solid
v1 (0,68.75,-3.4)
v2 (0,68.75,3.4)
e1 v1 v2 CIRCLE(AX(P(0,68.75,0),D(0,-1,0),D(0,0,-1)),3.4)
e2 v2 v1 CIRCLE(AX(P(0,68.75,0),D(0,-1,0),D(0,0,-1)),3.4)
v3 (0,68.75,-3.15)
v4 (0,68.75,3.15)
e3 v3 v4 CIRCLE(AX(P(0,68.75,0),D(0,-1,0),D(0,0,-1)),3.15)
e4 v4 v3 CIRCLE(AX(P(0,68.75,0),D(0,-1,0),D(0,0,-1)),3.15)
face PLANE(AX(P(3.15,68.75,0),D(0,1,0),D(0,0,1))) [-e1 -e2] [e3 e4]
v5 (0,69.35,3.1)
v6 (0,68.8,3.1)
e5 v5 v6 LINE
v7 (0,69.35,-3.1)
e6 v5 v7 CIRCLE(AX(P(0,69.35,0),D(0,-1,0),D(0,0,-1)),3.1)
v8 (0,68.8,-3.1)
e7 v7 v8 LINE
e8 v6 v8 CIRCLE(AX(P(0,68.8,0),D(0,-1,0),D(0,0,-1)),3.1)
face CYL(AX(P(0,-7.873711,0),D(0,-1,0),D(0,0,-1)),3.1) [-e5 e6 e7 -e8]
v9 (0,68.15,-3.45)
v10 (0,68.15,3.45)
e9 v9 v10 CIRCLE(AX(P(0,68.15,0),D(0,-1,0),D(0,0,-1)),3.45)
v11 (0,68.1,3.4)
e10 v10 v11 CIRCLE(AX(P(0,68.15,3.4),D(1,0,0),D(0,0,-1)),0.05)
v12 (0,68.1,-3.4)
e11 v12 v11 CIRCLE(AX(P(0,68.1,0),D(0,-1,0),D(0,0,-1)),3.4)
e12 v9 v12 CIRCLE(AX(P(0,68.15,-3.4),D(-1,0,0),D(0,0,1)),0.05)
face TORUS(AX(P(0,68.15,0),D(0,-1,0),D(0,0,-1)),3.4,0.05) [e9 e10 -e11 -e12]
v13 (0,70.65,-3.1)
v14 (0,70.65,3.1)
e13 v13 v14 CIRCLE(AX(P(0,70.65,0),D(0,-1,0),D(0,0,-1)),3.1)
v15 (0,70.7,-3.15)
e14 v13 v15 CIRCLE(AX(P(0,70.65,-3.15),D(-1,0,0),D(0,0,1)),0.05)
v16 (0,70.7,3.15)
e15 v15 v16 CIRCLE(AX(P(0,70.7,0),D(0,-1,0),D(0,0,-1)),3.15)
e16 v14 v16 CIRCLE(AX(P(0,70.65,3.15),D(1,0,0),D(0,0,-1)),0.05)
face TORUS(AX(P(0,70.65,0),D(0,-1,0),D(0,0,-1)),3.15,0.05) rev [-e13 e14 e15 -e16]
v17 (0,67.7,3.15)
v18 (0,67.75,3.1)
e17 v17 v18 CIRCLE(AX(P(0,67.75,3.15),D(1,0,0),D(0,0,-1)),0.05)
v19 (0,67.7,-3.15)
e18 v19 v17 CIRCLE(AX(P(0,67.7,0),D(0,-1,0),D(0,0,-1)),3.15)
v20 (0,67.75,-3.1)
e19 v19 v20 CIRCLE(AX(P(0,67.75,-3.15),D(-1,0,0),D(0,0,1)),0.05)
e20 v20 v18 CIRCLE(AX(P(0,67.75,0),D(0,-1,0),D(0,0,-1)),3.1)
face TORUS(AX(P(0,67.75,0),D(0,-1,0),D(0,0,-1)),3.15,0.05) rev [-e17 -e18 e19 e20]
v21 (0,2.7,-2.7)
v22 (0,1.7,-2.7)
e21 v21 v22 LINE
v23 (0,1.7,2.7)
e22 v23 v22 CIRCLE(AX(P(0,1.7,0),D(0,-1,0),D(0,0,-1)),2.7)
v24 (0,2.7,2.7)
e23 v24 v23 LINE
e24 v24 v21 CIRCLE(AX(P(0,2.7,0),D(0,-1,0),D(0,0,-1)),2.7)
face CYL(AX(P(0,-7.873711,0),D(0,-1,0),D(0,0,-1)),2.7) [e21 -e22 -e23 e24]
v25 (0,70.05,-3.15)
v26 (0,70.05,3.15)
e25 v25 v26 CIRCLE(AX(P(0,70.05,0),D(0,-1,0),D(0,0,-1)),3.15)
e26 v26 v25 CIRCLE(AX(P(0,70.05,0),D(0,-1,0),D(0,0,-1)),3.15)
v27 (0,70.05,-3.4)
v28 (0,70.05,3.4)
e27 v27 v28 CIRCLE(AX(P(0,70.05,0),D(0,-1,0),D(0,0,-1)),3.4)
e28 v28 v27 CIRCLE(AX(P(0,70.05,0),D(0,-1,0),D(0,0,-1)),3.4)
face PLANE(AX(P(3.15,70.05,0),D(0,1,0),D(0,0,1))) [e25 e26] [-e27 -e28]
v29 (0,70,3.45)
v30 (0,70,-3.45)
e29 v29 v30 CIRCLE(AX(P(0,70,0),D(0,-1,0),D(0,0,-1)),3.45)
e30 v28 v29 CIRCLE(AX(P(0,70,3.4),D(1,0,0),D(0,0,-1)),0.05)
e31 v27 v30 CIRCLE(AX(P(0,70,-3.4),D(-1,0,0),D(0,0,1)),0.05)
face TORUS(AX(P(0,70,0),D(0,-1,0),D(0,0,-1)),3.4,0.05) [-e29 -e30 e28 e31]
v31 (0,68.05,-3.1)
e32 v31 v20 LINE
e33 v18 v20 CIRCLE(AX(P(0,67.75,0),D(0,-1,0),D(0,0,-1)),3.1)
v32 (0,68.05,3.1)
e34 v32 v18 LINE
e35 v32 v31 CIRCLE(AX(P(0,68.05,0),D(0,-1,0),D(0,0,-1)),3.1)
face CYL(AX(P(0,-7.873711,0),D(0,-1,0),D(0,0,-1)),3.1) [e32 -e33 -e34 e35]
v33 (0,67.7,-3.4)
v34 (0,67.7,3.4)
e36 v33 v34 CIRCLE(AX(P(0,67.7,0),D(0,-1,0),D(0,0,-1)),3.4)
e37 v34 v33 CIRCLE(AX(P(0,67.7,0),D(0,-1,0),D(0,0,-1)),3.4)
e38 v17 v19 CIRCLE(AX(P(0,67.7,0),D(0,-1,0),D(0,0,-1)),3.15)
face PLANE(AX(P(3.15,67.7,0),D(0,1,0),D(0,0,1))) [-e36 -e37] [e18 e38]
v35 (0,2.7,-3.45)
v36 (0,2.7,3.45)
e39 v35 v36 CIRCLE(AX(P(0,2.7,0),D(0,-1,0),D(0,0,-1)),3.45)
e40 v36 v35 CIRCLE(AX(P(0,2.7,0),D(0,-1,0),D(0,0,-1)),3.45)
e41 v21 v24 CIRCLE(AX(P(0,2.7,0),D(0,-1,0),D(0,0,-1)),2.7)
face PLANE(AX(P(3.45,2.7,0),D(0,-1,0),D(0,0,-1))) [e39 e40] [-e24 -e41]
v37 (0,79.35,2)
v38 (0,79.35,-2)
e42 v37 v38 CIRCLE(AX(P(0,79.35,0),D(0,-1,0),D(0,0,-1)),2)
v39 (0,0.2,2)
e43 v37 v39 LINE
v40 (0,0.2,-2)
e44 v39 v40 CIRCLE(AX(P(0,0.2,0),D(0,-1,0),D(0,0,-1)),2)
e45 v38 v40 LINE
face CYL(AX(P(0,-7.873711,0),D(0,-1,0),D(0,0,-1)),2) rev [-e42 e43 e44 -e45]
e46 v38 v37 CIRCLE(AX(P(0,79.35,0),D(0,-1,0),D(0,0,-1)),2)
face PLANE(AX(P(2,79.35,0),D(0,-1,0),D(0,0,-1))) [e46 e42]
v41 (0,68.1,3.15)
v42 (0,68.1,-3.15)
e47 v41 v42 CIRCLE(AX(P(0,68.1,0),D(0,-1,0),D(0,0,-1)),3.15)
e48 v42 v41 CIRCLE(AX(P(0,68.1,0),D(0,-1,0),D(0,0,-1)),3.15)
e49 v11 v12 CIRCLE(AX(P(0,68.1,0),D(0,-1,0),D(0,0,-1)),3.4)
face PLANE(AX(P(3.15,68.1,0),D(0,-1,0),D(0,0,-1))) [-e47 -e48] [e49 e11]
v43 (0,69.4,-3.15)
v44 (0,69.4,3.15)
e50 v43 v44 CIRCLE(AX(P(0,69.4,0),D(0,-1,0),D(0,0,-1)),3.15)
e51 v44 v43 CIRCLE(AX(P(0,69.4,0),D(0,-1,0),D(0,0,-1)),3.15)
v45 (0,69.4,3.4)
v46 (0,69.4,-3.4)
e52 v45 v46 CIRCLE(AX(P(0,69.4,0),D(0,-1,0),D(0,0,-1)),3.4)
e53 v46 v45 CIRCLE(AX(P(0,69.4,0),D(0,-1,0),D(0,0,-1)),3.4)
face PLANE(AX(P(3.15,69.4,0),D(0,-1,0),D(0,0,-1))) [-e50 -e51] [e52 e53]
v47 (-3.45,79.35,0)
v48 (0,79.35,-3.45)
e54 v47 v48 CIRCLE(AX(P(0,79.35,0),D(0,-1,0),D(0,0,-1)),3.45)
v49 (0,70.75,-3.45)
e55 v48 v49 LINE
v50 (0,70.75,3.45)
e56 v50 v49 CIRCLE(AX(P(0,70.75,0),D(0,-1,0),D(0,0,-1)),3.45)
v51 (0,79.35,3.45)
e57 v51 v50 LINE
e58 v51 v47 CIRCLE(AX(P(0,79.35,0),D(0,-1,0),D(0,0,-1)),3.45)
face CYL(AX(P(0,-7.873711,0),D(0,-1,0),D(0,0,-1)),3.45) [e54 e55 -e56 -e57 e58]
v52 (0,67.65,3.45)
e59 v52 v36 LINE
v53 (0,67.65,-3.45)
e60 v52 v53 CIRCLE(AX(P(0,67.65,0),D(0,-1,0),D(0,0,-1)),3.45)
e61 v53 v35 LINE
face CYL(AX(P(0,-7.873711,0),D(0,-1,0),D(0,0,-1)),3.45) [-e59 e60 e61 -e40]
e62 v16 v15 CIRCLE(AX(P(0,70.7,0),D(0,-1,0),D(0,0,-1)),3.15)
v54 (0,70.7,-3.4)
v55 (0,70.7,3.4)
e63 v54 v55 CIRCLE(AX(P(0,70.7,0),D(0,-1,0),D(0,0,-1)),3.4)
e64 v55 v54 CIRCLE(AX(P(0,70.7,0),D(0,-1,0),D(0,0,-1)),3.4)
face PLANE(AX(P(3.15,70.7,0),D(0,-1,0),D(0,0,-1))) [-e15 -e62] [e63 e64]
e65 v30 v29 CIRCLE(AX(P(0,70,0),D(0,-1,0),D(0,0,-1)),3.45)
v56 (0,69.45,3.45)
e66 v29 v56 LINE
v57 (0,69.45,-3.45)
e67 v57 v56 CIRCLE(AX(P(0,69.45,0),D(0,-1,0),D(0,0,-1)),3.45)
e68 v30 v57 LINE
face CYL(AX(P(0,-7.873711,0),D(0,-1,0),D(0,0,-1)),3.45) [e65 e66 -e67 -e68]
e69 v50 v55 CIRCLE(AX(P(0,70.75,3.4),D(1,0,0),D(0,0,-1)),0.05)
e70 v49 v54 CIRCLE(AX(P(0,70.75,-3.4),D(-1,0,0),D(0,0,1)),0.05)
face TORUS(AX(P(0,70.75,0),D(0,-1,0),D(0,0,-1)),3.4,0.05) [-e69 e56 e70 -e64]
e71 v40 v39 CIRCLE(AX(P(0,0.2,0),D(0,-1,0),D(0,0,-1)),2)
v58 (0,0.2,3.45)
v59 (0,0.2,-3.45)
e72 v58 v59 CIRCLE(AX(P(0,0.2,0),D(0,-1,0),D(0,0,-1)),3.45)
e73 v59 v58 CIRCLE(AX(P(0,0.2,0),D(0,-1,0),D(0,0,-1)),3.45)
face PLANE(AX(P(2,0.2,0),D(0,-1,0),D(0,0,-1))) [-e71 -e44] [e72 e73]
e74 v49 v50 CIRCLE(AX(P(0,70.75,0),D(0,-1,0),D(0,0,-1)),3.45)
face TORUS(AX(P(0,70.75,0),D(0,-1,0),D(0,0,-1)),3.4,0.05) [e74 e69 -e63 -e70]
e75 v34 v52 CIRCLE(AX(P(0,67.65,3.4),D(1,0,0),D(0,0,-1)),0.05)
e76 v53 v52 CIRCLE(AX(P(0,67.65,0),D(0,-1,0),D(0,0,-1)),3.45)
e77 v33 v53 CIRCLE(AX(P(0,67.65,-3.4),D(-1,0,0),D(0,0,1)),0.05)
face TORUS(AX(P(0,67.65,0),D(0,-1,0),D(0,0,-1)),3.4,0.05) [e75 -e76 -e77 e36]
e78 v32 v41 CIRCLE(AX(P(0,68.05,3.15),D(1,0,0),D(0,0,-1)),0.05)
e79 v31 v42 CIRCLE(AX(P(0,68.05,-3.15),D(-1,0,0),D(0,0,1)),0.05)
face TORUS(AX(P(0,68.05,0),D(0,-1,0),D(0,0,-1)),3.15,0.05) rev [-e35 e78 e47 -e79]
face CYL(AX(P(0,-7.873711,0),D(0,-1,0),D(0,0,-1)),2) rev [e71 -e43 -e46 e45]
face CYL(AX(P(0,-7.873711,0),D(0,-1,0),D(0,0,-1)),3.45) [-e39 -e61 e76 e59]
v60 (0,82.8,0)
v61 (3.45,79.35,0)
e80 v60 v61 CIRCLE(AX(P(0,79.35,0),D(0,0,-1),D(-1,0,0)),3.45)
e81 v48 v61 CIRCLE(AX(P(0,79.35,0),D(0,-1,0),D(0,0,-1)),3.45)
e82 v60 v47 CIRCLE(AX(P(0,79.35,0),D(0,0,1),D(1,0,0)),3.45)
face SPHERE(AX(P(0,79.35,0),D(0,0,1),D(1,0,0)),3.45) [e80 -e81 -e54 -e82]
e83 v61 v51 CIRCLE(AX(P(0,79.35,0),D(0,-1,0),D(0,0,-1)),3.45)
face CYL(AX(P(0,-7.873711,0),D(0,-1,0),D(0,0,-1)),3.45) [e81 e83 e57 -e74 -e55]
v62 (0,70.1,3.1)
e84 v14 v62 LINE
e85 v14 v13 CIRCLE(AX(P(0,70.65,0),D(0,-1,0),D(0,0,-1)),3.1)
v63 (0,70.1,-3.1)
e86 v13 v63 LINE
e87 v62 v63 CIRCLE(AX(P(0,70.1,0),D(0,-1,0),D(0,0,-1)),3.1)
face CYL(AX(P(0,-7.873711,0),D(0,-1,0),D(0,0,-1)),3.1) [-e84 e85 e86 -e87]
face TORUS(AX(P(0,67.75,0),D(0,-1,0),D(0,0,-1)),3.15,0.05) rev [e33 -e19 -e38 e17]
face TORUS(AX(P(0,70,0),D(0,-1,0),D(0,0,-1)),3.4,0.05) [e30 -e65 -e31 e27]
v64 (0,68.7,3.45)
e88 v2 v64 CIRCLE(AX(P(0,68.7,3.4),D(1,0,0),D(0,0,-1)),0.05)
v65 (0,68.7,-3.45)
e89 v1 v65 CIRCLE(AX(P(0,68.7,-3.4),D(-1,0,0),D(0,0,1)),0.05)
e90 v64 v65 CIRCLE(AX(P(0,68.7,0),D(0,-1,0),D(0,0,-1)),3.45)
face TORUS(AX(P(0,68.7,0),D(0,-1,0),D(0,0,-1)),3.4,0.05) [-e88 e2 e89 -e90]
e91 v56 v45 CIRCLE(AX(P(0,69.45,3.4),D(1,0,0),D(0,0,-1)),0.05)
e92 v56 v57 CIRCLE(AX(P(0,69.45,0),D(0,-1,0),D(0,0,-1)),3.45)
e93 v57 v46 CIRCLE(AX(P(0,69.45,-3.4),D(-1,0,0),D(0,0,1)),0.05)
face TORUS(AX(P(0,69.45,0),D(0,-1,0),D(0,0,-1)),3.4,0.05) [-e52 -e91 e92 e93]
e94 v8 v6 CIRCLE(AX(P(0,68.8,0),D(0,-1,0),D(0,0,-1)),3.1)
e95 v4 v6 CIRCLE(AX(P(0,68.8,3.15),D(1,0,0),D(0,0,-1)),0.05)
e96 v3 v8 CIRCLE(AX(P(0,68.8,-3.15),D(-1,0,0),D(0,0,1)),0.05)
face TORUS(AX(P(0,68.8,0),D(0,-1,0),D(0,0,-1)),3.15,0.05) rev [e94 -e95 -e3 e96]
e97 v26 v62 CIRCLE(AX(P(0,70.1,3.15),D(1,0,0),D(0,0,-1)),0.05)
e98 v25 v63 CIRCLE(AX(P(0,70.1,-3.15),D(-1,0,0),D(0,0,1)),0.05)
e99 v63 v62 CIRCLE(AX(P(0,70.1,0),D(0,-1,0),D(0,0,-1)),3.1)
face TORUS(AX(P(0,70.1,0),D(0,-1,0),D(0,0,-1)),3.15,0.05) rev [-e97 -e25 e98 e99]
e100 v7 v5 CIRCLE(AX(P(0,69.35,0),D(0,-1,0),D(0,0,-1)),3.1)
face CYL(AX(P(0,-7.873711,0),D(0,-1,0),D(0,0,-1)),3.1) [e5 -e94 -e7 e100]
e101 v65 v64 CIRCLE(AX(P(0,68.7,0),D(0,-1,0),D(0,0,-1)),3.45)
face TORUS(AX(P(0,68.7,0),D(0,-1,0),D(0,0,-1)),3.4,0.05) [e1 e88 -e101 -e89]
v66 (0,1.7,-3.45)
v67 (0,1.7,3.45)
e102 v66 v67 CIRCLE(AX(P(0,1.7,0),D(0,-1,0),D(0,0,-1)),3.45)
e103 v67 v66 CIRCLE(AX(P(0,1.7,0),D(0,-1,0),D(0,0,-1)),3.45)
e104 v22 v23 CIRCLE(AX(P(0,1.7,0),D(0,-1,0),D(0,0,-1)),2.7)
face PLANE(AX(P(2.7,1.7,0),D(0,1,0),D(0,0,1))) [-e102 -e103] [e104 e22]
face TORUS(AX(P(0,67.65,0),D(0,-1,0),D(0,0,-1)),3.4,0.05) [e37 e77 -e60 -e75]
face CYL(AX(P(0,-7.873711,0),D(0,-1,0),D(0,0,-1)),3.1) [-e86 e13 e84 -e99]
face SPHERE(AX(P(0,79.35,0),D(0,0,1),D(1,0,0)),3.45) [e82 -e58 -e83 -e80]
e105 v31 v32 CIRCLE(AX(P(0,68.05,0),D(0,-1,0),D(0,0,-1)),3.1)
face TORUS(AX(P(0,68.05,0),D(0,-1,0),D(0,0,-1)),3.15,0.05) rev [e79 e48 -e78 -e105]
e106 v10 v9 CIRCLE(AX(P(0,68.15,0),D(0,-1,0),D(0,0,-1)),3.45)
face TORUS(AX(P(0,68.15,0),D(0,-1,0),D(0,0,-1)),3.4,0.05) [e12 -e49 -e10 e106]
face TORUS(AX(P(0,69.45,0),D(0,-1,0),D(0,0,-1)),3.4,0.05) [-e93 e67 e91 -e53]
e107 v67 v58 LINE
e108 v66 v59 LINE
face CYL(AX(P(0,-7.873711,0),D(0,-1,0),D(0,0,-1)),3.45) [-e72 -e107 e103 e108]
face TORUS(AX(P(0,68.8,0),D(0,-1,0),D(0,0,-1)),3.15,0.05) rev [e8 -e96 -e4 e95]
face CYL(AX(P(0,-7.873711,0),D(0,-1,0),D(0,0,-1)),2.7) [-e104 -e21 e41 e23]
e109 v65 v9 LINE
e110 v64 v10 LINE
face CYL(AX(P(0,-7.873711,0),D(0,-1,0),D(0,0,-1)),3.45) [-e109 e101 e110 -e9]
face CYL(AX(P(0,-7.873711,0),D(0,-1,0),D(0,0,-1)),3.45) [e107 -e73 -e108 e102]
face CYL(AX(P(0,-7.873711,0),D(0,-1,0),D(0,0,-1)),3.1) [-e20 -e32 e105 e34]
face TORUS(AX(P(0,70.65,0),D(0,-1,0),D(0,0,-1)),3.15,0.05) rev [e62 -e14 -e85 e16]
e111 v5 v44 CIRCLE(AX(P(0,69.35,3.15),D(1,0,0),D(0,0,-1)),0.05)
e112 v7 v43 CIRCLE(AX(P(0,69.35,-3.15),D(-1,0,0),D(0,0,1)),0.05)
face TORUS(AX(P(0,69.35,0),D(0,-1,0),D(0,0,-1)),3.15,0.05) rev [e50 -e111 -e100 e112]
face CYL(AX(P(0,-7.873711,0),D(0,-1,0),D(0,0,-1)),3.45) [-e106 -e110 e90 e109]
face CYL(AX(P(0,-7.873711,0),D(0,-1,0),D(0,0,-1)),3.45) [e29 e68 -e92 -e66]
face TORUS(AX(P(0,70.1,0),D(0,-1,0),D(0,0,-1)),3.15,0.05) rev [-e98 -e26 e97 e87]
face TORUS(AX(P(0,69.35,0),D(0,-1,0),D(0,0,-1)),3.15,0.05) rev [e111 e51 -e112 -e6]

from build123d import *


with BuildPart() as part:
    # Sketch1 → Revolve1 (revolve)
    with BuildSketch(Plane.XY, mode=Mode.PRIVATE) as revolve1_sk:
        with BuildLine():
            Line((2, 0.2), (3.45, 0.2))
            Line((3.45, 0.2), (3.45, 1.7))
            Line((3.45, 1.7), (2.7, 1.7))
            Line((2.7, 1.7), (2.7, 2.7))
            Line((2.7, 2.7), (3.45, 2.7))
            Line((3.45, 2.7), (3.45, 67.65))
            ThreePointArc((3.45, 67.65), (3.435355339, 67.685355339), (3.4, 67.7))
            Line((3.4, 67.7), (3.15, 67.7))
            ThreePointArc((3.15, 67.7), (3.114644661, 67.714644661), (3.1, 67.75))
            Line((3.1, 67.75), (3.1, 68.05))
            ThreePointArc((3.1, 68.05), (3.114644661, 68.085355339), (3.15, 68.1))
            Line((3.15, 68.1), (3.4, 68.1))
            ThreePointArc((3.4, 68.1), (3.435355339, 68.114644661), (3.45, 68.15))
            Line((3.45, 68.15), (3.45, 68.7))
            ThreePointArc((3.45, 68.7), (3.435355339, 68.735355339), (3.4, 68.75))
            Line((3.4, 68.75), (3.15, 68.75))
            ThreePointArc((3.15, 68.75), (3.114644661, 68.764644661), (3.1, 68.8))
            Line((3.1, 68.8), (3.1, 69.35))
            ThreePointArc((3.1, 69.35), (3.114644661, 69.385355339), (3.15, 69.4))
            Line((3.15, 69.4), (3.4, 69.4))
            ThreePointArc((3.4, 69.4), (3.435355339, 69.414644661), (3.45, 69.45))
            Line((3.45, 69.45), (3.45, 70))
            ThreePointArc((3.45, 70), (3.435355339, 70.035355339), (3.4, 70.05))
            Line((3.4, 70.05), (3.15, 70.05))
            ThreePointArc((3.15, 70.05), (3.114644661, 70.064644661), (3.1, 70.1))
            Line((3.1, 70.1), (3.1, 70.65))
            ThreePointArc((3.1, 70.65), (3.114644661, 70.685355339), (3.15, 70.7))
            Line((3.15, 70.7), (3.4, 70.7))
            ThreePointArc((3.4, 70.7), (3.435355339, 70.714644661), (3.45, 70.75))
            Line((3.45, 70.75), (3.45, 79.35))
            ThreePointArc((3.45, 79.35), (2.439518395, 81.789518395), (0, 82.8))
            Line((0, 82.8), (0, 79.35))
            Line((0, 79.35), (2, 79.35))
            Line((2, 79.35), (2, 0.2))
        make_face()
    revolve(revolve1_sk.sketch.rotate(Axis((0, -7.873710816, 0), (0, 1, 0)), 90), axis=Axis((0, -7.873710816, 0), (0, 1, 0)))


solid = part.part
